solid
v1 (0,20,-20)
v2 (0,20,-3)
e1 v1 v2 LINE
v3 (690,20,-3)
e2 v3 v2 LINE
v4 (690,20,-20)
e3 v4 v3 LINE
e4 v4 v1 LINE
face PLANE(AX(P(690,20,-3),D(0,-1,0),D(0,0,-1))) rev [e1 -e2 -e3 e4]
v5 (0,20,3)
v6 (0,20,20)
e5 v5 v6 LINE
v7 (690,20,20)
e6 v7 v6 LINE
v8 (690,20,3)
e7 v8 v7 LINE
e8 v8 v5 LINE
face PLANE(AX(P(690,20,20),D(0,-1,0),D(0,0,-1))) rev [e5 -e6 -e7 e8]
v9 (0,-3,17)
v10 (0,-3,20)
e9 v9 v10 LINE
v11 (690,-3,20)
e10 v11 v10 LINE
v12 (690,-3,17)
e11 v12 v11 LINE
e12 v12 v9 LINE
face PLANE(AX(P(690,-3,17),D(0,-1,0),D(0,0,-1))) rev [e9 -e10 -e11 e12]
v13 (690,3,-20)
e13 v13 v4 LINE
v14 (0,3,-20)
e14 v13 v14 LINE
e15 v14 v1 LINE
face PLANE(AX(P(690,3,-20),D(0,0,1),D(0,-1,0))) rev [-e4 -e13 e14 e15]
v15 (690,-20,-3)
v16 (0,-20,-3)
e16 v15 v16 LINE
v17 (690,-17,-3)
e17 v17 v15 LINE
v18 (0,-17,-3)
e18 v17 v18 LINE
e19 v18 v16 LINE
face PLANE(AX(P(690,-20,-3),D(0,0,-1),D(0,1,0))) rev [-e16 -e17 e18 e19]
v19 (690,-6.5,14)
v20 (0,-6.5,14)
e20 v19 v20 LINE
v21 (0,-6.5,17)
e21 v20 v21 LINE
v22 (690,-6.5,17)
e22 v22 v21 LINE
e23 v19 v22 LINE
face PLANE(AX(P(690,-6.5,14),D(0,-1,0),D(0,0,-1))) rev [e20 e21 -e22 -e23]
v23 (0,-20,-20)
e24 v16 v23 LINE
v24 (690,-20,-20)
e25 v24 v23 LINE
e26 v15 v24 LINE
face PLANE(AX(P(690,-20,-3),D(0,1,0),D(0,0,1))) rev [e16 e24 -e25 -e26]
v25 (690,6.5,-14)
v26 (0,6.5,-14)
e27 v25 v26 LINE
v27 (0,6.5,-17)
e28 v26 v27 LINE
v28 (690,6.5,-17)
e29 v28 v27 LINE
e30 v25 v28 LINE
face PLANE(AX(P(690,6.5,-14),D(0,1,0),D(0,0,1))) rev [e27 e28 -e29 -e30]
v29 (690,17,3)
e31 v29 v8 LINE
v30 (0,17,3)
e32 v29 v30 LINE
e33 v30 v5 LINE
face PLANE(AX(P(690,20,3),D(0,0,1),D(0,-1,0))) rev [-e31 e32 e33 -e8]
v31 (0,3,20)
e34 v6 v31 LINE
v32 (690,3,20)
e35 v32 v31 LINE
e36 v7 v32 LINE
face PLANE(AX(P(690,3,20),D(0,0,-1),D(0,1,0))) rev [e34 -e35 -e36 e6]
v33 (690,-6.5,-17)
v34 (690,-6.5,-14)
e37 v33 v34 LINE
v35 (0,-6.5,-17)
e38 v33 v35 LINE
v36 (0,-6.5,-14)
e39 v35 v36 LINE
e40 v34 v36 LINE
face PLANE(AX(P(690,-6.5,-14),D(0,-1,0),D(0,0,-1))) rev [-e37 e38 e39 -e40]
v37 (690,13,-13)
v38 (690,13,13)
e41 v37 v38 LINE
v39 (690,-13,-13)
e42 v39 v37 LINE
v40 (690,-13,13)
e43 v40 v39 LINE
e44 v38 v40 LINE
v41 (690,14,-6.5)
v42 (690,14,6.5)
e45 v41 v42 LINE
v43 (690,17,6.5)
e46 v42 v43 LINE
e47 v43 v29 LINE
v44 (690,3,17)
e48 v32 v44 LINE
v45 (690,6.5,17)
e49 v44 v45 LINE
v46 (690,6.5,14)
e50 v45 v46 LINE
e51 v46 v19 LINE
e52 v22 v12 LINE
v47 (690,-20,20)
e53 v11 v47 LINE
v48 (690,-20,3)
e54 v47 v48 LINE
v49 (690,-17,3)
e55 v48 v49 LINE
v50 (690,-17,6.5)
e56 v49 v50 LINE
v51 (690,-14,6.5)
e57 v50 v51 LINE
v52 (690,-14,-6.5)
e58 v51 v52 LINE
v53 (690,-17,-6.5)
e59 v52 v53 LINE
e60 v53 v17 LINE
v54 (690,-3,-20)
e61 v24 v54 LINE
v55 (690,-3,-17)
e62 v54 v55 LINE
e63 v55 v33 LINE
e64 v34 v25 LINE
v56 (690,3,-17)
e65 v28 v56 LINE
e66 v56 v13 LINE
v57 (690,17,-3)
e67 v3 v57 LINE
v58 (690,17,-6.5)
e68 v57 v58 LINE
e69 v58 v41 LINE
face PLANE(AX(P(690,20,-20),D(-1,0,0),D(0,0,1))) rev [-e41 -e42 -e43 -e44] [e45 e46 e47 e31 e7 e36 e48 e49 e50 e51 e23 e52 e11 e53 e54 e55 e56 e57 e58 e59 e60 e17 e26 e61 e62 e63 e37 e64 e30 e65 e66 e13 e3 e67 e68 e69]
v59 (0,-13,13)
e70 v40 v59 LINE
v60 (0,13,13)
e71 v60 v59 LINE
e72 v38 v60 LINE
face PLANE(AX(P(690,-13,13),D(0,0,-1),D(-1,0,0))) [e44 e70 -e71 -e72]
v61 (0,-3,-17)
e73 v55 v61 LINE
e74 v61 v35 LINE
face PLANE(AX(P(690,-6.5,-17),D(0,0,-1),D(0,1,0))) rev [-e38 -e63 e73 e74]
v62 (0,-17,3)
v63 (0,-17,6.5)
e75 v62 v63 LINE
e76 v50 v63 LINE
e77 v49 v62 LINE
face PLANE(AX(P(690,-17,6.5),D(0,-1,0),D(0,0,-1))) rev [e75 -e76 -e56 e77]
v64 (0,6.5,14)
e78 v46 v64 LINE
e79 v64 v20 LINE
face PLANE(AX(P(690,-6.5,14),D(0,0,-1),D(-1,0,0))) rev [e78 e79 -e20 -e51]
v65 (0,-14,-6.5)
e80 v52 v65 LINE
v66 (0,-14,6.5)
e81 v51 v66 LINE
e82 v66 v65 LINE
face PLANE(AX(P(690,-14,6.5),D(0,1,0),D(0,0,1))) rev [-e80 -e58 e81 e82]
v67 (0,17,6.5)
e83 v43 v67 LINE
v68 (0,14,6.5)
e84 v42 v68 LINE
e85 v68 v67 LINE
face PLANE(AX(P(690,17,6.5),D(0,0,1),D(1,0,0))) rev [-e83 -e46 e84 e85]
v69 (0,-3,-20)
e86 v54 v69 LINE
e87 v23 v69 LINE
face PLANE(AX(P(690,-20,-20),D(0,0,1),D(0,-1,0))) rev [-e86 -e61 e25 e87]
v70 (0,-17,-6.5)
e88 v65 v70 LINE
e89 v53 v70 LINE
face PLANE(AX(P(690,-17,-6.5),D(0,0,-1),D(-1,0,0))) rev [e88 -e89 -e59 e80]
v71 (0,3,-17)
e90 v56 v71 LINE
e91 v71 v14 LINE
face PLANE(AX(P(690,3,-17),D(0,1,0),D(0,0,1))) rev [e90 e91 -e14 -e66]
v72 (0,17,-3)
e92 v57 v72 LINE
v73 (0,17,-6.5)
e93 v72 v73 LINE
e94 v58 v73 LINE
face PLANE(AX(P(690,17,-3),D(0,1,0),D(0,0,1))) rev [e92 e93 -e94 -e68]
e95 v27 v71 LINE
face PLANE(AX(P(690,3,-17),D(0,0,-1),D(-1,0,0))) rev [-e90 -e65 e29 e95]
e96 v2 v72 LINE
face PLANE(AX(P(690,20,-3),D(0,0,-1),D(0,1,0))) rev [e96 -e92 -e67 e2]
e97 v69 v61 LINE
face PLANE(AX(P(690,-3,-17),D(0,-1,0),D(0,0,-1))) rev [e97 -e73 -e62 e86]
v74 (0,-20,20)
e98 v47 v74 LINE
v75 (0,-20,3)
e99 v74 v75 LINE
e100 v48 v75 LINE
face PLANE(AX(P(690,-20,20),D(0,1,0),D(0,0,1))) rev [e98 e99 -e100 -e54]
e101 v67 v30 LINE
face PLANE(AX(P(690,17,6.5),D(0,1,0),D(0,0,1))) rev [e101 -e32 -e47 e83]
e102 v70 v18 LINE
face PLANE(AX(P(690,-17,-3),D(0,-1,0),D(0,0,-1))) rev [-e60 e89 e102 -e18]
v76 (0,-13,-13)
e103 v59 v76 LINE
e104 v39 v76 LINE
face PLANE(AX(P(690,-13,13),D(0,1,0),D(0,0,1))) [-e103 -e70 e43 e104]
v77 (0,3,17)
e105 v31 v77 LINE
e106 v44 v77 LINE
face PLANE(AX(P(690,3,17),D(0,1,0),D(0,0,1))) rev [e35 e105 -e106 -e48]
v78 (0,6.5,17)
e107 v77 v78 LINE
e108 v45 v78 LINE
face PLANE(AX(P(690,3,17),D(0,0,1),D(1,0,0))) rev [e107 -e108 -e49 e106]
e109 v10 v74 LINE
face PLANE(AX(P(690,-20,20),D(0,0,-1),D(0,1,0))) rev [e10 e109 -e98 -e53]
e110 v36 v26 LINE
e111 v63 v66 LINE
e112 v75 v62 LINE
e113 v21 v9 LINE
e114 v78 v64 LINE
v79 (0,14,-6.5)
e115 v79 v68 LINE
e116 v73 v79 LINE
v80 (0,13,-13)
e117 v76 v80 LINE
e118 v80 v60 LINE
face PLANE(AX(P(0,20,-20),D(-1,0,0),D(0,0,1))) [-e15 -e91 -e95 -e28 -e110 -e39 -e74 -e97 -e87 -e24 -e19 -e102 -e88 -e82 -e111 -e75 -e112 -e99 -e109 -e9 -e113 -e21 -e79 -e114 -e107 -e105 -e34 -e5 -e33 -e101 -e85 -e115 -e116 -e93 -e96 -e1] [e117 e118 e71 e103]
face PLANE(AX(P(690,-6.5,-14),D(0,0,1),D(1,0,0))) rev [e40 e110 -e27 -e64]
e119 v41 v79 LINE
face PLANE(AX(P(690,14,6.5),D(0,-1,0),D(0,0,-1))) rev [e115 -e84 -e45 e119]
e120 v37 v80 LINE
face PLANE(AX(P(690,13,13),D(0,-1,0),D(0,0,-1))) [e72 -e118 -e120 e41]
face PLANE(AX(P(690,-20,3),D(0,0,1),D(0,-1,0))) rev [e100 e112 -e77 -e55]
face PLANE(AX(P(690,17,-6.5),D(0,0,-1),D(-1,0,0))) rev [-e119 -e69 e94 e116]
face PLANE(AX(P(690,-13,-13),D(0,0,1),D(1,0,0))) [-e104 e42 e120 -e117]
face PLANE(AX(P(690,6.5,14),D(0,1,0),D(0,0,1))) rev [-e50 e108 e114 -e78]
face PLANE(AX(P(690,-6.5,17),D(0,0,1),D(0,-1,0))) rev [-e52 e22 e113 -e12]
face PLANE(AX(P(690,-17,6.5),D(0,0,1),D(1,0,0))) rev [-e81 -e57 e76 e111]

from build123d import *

# Parameters (mm, degrees)
SKETCH1_W           = 26
SKETCH1_H           = 26
BOSS_EXTRUDE1_DEPTH = 690


with BuildPart() as part:
    # Sketch1 → Boss-Extrude1 (new body)
    with BuildSketch(Plane(origin=(0, 0, 0), x_dir=(0, 0, -1), z_dir=(1, 0, 0))):
        Polygon((-20, -20), (-3, -20), (-3, -17), (-6.5, -17), (-6.5, -14), (6.5, -14), (6.5, -17), (3, -17), (3, -20), (20, -20), (20, -3), (17, -3), (17, -6.5), (14, -6.5), (14, 6.5), (17, 6.5), (17, 3), (20, 3), (20, 20), (3, 20), (3, 17), (6.5, 17), (6.5, 14), (-6.5, 14), (-6.5, 17), (-3, 17), (-3, 20), (-20, 20), (-20, 3), (-17, 3), (-17, 6.5), (-14, 6.5), (-14, -6.5), (-17, -6.5), (-17, -3), (-20, -3), align=None)
        Rectangle(SKETCH1_W, SKETCH1_H, mode=Mode.SUBTRACT)
    extrude(amount=BOSS_EXTRUDE1_DEPTH)


solid = part.part
